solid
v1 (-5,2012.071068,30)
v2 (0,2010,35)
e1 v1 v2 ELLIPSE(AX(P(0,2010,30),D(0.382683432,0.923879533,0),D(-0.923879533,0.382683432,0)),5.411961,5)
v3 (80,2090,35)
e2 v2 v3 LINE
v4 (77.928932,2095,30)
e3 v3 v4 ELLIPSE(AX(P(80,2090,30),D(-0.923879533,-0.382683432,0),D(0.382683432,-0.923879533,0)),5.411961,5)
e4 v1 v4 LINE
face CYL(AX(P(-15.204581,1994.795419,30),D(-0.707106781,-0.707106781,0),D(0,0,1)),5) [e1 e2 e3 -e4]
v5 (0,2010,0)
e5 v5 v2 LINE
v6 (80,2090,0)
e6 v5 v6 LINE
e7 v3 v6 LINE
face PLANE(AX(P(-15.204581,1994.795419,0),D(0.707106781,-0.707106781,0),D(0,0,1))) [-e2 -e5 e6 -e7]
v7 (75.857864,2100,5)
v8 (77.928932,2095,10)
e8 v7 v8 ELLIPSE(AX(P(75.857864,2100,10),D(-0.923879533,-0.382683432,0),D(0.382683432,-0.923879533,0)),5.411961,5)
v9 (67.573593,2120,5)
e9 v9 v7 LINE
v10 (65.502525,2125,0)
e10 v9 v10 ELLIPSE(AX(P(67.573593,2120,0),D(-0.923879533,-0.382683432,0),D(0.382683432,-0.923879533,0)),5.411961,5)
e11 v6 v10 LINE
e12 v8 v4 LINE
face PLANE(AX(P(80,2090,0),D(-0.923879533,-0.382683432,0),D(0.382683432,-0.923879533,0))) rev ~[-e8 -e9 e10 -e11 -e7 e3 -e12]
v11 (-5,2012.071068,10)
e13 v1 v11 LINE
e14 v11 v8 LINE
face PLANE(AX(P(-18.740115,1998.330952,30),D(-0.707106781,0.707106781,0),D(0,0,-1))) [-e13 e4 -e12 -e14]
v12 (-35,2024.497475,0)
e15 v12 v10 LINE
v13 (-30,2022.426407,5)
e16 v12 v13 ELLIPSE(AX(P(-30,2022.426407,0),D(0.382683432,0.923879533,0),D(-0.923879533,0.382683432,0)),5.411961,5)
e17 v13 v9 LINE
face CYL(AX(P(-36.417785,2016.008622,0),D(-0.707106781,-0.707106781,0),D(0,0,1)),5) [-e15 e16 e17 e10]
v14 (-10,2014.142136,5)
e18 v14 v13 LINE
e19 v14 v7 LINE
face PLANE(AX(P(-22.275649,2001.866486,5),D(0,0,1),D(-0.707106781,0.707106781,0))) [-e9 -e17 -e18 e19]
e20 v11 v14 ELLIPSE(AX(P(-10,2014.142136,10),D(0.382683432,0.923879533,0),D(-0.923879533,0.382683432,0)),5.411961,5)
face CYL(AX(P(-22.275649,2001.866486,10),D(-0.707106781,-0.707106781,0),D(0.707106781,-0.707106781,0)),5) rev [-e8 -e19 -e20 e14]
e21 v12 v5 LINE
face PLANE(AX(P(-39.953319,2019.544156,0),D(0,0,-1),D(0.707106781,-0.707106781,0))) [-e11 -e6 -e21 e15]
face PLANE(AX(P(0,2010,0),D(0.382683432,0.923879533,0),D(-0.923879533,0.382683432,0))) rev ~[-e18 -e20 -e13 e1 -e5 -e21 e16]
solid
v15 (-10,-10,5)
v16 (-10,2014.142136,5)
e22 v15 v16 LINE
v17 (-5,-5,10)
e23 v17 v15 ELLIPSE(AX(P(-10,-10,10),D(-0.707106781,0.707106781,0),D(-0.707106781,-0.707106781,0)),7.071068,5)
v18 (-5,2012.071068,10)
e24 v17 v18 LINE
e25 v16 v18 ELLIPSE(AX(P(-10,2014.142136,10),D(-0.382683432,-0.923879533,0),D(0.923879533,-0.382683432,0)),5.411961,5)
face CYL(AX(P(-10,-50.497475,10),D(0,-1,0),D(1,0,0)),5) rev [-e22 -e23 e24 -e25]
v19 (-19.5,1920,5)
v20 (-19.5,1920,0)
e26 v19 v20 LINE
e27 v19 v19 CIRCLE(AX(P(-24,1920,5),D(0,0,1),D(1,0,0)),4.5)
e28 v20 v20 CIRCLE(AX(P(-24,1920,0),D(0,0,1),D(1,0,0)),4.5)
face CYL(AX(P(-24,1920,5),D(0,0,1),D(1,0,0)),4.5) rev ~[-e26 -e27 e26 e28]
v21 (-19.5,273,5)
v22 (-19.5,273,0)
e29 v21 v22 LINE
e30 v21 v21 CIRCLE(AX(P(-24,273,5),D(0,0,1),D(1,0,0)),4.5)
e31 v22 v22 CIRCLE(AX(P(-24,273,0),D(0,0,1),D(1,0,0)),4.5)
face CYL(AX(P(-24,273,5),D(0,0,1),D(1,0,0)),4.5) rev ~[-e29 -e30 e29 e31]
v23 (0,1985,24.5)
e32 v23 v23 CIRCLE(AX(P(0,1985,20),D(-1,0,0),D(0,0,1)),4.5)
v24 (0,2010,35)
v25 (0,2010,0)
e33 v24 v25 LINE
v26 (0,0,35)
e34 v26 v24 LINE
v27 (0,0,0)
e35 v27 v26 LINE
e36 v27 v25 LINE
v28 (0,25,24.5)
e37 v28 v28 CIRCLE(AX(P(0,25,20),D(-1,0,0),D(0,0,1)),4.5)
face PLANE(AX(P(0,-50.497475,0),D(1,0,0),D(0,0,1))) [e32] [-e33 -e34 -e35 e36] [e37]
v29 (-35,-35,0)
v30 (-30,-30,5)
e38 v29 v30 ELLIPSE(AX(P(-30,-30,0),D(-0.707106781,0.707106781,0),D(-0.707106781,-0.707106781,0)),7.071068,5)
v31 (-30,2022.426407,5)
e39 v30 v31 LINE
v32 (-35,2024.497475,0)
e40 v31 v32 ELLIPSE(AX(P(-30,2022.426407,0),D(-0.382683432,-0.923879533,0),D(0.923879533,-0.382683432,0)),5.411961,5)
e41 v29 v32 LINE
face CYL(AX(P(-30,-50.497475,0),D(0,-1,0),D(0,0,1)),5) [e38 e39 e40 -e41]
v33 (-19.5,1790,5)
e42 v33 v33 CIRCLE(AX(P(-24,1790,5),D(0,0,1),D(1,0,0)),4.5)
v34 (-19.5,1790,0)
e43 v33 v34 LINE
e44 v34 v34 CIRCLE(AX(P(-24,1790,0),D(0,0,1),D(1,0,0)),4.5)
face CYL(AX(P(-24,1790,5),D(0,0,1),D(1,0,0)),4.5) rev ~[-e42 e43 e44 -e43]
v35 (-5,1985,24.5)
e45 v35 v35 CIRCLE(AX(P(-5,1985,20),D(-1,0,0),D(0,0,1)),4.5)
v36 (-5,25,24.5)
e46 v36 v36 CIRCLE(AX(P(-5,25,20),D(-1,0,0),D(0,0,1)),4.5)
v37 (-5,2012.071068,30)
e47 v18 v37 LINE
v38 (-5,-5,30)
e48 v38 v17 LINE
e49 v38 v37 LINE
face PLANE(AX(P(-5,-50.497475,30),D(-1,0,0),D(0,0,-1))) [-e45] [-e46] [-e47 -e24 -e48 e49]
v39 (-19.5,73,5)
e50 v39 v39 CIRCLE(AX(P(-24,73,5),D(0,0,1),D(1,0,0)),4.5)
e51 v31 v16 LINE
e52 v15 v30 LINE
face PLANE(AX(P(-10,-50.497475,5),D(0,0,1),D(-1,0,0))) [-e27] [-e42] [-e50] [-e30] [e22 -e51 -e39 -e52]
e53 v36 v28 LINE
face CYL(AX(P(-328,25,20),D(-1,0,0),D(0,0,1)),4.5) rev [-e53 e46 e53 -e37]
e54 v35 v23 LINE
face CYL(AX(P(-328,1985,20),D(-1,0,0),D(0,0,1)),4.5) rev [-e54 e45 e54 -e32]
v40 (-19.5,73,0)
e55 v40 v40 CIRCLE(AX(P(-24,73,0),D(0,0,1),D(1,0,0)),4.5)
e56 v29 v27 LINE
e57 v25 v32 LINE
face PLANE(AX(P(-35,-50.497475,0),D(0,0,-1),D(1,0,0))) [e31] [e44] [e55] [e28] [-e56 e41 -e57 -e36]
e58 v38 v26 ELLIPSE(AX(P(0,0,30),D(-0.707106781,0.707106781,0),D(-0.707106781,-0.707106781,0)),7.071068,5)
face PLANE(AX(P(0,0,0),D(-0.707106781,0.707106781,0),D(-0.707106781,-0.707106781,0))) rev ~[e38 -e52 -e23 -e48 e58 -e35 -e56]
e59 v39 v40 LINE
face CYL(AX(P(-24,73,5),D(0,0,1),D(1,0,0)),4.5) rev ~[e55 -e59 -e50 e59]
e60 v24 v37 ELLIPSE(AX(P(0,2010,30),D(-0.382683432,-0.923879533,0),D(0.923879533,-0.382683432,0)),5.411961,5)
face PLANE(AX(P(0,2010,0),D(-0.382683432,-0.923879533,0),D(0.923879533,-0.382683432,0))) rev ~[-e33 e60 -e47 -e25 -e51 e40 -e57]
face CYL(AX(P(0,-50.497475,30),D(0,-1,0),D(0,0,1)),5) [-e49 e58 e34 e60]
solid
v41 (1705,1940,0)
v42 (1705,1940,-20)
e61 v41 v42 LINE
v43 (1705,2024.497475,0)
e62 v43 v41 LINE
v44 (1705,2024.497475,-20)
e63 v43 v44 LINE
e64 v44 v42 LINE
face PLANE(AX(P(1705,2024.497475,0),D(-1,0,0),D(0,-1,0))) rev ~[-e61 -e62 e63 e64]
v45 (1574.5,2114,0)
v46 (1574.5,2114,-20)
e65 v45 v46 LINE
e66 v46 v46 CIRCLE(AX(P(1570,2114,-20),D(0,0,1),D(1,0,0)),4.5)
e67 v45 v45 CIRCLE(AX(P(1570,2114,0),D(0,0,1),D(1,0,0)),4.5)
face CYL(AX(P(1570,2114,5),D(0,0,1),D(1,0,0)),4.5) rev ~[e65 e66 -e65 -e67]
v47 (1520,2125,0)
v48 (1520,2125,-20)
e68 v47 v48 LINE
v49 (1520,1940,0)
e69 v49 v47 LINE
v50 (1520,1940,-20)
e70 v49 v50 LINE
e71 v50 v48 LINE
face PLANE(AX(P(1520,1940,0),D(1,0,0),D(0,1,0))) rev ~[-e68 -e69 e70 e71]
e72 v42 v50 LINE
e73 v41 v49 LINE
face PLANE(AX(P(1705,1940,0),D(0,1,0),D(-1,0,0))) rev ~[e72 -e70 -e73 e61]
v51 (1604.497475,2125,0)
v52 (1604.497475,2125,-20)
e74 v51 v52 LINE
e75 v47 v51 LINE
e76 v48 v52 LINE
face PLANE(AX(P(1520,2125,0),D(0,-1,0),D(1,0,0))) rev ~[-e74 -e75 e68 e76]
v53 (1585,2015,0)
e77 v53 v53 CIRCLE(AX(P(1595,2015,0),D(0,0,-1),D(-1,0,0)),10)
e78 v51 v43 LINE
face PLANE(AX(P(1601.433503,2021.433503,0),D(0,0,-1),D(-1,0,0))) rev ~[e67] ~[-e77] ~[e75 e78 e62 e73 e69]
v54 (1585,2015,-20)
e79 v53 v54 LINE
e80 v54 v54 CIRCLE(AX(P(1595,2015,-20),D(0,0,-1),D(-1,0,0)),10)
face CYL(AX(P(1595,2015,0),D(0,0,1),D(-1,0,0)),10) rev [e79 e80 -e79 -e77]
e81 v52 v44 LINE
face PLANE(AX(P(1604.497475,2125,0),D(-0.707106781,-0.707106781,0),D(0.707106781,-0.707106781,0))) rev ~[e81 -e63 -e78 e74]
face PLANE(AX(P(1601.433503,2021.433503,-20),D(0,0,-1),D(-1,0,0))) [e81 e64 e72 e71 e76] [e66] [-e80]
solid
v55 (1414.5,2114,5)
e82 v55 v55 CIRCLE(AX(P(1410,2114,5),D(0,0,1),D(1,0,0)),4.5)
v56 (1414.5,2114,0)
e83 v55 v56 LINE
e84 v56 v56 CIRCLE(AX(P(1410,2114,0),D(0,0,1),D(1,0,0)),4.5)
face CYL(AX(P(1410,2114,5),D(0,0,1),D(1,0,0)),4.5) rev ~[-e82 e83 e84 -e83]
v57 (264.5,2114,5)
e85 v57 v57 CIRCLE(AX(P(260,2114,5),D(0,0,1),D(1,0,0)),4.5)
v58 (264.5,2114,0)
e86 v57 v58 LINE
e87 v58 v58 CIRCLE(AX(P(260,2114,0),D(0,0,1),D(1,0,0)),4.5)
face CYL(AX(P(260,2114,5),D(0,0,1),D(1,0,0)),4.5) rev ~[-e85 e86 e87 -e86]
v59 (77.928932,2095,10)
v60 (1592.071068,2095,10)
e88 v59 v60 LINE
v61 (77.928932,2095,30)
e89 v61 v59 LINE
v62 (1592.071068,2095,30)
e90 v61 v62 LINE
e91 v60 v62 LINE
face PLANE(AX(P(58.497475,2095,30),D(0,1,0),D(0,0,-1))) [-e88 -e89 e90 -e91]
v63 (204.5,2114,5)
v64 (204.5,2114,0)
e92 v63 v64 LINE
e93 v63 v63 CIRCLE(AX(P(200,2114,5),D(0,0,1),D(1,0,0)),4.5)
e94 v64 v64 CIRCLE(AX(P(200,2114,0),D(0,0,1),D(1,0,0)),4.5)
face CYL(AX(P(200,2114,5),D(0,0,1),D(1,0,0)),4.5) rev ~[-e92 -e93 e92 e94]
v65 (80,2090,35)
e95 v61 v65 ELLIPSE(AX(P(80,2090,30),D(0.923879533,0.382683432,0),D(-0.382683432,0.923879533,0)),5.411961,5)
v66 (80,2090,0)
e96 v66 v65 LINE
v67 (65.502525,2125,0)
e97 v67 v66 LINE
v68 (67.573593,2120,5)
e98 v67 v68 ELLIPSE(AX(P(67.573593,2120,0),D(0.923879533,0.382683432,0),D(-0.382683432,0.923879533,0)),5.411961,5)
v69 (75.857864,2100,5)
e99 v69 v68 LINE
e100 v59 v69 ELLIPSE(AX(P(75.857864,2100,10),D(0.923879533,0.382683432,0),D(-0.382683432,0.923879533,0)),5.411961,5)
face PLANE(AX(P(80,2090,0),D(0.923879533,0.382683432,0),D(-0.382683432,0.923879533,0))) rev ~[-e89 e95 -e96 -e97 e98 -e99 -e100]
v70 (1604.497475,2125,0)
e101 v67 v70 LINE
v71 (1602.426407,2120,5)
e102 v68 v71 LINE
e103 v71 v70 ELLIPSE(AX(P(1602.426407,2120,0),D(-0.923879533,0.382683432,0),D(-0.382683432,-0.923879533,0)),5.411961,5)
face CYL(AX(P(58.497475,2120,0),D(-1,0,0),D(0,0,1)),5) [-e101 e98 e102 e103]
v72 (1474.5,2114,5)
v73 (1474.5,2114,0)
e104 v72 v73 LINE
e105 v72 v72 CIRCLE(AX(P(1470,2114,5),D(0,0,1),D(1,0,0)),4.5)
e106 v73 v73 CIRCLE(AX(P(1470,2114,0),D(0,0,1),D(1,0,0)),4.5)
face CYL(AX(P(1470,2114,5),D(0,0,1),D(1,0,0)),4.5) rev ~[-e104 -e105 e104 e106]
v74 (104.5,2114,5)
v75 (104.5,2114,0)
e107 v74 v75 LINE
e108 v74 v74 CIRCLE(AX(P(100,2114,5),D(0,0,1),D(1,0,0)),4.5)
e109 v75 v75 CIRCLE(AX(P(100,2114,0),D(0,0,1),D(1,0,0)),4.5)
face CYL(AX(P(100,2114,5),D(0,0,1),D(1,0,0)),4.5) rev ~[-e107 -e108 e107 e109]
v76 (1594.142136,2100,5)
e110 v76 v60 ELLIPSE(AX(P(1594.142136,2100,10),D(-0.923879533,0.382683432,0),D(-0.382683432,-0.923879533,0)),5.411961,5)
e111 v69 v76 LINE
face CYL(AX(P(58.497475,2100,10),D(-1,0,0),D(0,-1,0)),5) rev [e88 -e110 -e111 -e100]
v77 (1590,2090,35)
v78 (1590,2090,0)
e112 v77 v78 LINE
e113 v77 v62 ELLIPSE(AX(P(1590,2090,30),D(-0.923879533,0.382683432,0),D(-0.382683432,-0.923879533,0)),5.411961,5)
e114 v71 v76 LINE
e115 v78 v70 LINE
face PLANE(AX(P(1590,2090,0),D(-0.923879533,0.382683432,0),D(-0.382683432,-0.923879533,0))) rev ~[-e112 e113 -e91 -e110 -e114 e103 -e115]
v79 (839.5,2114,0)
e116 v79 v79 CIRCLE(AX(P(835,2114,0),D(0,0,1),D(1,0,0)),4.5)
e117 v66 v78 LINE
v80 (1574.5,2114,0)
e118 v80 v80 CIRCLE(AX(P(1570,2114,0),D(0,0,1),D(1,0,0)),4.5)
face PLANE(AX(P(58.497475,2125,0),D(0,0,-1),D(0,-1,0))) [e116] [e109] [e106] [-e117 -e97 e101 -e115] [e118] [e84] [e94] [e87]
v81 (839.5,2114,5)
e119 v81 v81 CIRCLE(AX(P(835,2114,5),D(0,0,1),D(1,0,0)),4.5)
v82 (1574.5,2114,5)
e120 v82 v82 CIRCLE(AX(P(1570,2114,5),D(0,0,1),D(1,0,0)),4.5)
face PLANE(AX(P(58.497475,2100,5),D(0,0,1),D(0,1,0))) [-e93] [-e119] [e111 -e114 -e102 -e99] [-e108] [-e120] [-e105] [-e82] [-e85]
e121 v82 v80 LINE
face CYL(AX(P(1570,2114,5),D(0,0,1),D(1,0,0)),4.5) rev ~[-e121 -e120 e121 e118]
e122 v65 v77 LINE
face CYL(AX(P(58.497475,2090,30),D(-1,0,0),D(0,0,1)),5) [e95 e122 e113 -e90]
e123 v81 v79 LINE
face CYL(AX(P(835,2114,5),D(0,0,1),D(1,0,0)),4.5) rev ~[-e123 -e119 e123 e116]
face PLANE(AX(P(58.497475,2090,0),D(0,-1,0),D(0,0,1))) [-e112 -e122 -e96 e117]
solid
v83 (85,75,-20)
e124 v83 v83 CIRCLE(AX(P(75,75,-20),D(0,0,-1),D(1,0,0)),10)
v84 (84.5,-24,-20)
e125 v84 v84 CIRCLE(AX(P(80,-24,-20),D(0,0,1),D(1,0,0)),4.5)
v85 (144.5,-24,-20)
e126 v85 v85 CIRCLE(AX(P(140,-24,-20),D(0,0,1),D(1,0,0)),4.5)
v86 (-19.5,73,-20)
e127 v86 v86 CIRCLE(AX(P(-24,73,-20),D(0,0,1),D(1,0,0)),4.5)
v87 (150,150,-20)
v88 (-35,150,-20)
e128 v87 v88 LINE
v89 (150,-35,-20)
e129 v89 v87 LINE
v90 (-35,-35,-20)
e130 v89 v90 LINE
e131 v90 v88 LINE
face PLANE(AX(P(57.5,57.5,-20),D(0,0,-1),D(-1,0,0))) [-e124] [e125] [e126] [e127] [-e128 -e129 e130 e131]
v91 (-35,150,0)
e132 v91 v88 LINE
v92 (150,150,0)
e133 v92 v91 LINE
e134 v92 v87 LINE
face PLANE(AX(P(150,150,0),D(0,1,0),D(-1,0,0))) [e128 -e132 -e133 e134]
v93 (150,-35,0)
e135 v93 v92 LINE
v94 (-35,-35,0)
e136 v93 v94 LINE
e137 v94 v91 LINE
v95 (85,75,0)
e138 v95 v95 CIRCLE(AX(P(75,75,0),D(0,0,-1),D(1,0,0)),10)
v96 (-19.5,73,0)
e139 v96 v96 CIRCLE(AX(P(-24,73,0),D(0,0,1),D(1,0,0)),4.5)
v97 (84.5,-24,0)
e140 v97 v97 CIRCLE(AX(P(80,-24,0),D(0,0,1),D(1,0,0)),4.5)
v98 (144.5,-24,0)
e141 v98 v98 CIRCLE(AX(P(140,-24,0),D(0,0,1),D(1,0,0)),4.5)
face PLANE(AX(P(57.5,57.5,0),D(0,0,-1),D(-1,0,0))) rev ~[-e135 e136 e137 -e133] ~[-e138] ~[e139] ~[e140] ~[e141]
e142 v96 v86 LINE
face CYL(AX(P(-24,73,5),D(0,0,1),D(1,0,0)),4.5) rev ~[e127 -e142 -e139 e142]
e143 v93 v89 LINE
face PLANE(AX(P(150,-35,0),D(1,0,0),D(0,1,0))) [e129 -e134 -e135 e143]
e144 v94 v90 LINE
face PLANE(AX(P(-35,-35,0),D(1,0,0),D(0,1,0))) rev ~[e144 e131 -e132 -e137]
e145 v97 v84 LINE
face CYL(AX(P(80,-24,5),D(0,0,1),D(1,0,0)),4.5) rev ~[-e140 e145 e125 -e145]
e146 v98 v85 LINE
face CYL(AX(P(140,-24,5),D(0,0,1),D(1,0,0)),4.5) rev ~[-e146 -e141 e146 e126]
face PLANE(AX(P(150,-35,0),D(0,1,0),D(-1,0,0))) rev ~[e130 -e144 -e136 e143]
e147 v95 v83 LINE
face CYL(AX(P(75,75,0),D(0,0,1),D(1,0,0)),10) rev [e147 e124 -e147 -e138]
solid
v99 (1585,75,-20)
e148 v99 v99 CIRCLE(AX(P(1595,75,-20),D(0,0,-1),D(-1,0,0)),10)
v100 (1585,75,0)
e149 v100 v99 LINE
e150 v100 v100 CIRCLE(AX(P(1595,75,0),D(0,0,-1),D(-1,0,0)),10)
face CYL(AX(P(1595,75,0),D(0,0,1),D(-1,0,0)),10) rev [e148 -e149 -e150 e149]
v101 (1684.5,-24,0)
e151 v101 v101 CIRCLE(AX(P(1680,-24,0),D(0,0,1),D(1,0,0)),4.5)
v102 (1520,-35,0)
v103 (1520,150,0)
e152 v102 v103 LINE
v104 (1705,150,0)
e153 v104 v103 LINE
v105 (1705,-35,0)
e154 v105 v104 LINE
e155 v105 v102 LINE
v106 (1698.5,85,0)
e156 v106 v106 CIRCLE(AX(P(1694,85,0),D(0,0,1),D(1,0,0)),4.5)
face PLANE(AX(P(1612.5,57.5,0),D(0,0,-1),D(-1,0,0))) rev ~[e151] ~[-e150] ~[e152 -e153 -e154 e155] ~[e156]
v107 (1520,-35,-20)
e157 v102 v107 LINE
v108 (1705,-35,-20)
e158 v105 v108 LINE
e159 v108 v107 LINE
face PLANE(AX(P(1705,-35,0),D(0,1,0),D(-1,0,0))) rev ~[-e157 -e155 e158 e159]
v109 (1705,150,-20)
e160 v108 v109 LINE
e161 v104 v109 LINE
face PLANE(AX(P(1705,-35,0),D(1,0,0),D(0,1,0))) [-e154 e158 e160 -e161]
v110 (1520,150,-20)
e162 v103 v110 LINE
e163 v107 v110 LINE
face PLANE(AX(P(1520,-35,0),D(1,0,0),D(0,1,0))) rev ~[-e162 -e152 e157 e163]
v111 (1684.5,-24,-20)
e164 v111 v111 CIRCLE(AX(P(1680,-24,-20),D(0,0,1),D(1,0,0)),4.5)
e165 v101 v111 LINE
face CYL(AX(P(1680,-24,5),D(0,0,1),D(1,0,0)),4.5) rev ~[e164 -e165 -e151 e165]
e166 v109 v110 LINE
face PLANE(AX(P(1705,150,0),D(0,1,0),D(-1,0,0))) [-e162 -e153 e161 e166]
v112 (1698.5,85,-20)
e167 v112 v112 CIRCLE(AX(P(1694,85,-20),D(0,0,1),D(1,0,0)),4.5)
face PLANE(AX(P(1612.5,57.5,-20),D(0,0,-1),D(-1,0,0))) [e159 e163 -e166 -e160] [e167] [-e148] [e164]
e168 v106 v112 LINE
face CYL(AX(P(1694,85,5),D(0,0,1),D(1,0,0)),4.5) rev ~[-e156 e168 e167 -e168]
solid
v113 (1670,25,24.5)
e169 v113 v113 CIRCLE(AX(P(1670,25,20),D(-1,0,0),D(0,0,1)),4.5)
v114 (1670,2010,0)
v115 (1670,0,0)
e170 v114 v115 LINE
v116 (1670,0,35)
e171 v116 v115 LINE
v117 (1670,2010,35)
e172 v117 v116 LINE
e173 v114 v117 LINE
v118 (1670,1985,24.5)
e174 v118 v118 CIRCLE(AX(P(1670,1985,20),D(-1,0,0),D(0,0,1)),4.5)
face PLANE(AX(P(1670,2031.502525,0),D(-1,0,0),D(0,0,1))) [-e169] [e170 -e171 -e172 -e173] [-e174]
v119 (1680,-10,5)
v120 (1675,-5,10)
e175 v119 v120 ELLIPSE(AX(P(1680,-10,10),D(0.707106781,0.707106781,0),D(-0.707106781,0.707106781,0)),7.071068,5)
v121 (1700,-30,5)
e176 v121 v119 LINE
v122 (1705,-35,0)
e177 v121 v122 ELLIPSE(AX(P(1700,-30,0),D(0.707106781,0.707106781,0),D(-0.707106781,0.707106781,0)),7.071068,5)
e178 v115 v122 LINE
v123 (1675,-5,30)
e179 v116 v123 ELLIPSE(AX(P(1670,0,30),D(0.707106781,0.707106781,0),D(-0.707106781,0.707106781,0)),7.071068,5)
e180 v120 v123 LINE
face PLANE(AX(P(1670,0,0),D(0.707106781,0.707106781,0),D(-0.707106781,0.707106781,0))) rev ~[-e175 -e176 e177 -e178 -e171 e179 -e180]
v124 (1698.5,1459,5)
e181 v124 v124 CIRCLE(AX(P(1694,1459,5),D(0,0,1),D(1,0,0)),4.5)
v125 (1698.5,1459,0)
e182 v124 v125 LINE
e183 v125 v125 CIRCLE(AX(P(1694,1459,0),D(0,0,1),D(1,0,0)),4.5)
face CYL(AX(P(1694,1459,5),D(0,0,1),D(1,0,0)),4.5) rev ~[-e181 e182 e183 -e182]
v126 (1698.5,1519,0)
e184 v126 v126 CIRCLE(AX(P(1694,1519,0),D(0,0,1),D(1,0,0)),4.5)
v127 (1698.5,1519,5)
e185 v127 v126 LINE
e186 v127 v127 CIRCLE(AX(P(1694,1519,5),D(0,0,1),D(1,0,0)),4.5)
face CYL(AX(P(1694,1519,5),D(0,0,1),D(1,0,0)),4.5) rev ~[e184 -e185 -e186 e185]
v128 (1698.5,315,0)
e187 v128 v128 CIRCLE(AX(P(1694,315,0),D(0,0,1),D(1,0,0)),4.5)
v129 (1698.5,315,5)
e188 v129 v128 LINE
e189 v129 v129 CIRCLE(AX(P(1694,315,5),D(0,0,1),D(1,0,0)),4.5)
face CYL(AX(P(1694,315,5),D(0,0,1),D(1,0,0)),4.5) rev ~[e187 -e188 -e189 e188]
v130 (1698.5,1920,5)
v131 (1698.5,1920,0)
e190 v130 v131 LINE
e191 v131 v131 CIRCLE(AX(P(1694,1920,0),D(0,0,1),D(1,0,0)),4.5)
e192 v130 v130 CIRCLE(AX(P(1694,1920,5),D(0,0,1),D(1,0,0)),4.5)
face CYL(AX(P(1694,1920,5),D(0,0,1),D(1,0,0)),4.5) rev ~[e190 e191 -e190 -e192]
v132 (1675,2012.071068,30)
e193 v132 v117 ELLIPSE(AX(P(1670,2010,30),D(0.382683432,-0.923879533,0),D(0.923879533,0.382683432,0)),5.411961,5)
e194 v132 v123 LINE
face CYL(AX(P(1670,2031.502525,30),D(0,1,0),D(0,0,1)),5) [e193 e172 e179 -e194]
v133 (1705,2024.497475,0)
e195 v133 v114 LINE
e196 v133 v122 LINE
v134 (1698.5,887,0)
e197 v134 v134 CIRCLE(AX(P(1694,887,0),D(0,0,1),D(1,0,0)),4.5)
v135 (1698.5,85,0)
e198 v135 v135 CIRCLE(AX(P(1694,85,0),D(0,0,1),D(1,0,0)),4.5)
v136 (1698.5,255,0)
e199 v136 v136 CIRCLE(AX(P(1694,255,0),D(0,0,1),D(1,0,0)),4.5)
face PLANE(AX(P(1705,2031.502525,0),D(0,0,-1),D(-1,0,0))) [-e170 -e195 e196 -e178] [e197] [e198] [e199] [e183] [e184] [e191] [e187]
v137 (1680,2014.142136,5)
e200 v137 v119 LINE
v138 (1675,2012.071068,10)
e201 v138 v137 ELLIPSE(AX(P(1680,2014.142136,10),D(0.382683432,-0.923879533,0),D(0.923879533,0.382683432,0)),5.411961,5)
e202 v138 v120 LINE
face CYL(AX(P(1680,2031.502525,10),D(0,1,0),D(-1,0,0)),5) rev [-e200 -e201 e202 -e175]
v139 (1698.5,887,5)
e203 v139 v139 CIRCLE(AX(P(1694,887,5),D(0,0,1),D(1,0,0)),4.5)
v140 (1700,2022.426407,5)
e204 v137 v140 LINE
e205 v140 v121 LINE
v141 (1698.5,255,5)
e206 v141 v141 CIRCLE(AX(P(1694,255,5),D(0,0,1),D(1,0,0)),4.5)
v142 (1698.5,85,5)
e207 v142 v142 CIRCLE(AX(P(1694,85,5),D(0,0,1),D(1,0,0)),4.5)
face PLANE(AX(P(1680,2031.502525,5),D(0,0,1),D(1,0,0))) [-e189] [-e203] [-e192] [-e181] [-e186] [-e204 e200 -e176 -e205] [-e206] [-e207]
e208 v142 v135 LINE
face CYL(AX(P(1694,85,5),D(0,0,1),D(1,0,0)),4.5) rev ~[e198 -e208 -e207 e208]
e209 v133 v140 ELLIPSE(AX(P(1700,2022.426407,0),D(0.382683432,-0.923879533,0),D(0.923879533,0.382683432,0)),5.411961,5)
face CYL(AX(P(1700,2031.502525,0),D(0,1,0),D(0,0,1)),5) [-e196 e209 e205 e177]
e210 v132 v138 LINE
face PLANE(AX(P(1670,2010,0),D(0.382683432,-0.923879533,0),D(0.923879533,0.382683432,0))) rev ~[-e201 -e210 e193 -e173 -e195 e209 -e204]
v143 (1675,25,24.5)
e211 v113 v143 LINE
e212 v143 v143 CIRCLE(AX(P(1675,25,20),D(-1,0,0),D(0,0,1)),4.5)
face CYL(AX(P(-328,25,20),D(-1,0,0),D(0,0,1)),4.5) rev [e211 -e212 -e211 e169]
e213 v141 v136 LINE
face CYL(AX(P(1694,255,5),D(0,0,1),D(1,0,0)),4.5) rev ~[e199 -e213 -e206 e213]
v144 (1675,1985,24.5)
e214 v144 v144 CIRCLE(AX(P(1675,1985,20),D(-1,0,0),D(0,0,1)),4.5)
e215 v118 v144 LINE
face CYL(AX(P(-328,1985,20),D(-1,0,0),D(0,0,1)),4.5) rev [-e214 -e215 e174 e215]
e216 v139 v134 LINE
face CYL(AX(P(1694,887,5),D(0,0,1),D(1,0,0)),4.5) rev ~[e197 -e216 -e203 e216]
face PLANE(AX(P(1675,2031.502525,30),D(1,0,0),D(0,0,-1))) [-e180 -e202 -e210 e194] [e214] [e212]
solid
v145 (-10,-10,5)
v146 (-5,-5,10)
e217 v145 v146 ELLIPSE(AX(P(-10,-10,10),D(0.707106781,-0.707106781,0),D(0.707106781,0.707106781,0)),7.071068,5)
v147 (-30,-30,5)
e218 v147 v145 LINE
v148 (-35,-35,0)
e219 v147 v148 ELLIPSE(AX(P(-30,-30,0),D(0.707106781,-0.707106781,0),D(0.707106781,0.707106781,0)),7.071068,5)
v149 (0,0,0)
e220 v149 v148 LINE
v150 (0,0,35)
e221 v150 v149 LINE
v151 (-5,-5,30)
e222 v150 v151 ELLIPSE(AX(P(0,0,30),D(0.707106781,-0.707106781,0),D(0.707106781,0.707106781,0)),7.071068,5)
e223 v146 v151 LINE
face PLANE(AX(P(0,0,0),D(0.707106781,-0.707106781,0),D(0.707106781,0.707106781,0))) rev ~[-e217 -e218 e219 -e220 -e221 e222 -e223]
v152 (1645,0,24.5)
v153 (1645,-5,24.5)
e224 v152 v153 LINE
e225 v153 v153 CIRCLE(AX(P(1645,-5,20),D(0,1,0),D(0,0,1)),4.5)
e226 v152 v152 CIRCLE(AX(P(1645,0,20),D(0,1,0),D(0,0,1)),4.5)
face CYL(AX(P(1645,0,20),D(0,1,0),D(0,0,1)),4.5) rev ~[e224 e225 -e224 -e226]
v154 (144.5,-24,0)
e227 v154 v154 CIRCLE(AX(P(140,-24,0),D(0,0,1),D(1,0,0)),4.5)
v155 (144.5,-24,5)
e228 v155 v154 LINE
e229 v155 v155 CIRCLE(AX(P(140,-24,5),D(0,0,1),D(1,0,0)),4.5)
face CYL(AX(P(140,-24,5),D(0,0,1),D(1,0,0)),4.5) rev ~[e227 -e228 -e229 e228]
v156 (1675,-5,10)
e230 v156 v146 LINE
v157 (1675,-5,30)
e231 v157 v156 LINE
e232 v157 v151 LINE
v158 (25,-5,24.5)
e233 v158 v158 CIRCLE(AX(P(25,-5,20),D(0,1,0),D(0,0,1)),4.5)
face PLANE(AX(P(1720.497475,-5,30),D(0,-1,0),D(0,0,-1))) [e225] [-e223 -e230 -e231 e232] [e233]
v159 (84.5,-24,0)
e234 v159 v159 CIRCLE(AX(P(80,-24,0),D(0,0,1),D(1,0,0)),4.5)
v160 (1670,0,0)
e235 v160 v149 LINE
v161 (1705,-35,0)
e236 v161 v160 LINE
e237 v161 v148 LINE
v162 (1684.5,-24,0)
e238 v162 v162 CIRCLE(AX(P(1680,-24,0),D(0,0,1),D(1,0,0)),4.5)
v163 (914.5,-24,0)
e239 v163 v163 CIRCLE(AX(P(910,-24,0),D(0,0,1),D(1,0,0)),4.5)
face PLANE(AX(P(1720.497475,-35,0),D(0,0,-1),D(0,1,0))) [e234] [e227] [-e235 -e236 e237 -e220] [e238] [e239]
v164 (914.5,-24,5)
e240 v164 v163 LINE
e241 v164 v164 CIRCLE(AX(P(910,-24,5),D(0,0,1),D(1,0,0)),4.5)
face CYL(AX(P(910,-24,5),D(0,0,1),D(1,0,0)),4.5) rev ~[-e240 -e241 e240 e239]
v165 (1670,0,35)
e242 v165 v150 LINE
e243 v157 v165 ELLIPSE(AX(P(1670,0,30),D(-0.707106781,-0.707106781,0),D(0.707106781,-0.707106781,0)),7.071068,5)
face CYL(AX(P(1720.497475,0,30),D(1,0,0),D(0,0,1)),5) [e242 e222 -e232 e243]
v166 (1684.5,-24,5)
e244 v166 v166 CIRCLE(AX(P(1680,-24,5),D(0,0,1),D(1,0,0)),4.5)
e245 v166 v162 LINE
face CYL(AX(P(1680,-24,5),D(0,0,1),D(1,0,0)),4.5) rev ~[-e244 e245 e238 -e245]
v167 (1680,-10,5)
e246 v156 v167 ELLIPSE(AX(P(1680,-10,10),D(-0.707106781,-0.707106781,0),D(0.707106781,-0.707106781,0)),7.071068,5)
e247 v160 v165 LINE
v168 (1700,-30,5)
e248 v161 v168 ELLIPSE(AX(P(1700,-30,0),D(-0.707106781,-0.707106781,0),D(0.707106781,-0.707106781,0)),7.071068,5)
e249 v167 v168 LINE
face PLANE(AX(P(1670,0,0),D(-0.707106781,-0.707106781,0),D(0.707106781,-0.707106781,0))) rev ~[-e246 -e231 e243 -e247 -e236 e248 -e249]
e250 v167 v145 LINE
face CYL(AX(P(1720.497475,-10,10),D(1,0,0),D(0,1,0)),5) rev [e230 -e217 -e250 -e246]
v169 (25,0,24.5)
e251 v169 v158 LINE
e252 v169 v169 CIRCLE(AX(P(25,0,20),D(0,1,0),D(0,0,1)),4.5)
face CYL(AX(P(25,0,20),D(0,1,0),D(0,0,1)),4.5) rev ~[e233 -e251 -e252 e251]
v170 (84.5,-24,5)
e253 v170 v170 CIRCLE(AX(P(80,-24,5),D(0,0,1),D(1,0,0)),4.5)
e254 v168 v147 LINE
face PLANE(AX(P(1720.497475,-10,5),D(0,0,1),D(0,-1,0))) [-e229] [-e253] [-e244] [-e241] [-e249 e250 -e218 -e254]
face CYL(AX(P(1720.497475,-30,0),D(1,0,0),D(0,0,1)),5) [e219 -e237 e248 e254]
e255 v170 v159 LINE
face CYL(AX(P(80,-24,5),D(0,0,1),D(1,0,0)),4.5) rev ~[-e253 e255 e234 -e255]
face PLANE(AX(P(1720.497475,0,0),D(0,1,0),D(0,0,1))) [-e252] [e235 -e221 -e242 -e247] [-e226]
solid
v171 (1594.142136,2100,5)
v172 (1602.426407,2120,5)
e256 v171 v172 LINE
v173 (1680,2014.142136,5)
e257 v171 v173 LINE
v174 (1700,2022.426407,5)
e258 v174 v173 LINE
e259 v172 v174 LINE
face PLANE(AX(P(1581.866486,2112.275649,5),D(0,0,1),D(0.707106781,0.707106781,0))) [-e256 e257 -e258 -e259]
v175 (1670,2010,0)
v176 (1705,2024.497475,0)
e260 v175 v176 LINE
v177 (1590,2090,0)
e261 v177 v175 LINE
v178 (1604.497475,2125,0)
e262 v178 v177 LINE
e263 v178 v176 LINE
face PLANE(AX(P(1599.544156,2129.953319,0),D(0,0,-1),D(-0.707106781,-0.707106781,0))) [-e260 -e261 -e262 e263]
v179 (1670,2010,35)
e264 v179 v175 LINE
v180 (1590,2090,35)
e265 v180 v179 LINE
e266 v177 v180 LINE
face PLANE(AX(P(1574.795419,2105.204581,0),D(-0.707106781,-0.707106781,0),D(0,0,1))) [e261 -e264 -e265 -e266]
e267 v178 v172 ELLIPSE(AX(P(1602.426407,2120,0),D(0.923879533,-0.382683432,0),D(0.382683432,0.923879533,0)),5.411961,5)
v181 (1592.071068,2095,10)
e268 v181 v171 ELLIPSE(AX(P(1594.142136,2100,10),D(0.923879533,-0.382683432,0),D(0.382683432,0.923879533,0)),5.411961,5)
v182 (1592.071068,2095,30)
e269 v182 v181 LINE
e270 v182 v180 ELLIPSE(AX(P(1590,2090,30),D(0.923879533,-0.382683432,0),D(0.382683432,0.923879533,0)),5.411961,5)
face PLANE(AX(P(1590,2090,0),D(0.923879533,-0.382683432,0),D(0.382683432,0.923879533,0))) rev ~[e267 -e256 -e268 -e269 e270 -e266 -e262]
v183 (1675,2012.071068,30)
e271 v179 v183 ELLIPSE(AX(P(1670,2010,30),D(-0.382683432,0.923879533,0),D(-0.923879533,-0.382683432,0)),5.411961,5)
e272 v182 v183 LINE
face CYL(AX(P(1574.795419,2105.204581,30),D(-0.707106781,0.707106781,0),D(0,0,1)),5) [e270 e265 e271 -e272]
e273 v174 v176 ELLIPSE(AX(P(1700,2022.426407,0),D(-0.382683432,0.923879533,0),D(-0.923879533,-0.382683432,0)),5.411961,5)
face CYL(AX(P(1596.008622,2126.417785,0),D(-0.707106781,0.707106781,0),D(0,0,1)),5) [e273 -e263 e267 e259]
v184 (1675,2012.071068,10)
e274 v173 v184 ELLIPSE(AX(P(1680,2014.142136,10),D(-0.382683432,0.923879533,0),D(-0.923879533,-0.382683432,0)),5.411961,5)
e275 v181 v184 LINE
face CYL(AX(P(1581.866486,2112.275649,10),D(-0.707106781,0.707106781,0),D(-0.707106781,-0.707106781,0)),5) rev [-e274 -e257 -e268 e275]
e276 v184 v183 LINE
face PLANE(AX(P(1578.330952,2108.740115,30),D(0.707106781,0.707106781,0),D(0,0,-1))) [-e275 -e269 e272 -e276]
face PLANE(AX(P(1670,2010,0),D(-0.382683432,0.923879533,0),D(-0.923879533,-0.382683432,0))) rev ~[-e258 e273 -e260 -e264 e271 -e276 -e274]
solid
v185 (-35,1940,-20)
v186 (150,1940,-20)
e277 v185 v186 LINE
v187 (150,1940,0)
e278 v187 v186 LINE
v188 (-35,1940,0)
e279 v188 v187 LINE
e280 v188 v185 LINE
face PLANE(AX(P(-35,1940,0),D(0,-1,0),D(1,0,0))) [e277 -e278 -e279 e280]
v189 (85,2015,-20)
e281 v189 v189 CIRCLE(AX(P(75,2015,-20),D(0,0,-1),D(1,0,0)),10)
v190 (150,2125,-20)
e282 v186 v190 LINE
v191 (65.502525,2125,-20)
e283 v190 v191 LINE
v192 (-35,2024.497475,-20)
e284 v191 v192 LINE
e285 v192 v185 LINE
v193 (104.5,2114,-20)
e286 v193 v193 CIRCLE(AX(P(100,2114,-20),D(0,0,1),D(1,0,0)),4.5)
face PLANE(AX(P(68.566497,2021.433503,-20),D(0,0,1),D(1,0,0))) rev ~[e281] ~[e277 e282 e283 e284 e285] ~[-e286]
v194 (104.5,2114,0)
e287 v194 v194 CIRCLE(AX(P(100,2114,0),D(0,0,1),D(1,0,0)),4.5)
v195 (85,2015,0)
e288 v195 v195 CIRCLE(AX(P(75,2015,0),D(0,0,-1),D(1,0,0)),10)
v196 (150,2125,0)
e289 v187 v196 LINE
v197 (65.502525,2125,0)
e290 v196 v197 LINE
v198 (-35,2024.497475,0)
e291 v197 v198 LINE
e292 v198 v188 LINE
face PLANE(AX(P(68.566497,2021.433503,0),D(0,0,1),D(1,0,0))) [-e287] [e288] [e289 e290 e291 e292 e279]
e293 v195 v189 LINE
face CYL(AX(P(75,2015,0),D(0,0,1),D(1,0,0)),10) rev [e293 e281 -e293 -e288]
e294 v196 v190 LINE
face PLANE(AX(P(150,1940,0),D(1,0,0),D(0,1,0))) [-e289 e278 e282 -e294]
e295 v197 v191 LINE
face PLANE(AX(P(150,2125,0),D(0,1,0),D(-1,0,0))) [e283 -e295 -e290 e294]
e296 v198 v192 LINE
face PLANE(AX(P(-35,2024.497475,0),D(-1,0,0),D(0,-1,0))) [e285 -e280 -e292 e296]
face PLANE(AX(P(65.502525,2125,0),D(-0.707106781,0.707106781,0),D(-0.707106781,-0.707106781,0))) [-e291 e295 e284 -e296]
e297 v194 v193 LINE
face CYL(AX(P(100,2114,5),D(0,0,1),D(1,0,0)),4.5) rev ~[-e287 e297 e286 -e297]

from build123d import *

# Parameters (mm, degrees)
MEMBER_1_DEPTH           = 2031.502525317
MEMBER_1_DEPTH_BACK      = 50.497474683
MEMBER_1_2_DEPTH         = 156.142135624
MEMBER_1_3_DEPTH         = 1553.005050634
MEMBER_1_4_DEPTH         = 156.142135624
MEMBER_1_5_DEPTH         = 2082
MEMBER_1_6_DEPTH         = 1770.994949366
SKETCH_3_R               = 10
EXTRUDE_1_DEPTH          = 20
SKETCH_3_W               = 185
SKETCH_3_H               = 185
EXTRUDE_1_2_DEPTH        = 20
EXTRUDE_1_3_DEPTH        = 20
EXTRUDE_1_4_DEPTH        = 20
SKETCH_4_R               = 4.5
CUT_EXTRUDE_1_DEPTH      = 10
CUT_EXTRUDE_2_DEPTH      = 2262
CUT_EXTRUDE_2_DEPTH_BACK = 328
SKETCH_5_R               = 4.5
SKETCH_6_R               = 4.5
CUT_EXTRUDE_3_DEPTH      = 236
SKETCH_7_R               = 4.5
CUT_EXTRUDE_4_DEPTH      = 228
SKETCH_8_R               = 4.5
CUT_EXTRUDE_5_DEPTH      = 99
SKETCH_9_R               = 4.5
CUT_EXTRUDE_6_DEPTH      = 78


with BuildPart() as part:
    # Sketch1 → Member 1 (new, two sides: drawn at the far end of the back side and taken through both)
    with BuildSketch(Plane(origin=(0, 0, 0), x_dir=(-1, 0, 0), z_dir=(0, 1, 0)).offset(-MEMBER_1_DEPTH_BACK)):
        with BuildLine():
            Line((0, 0), (0, 35))
            ThreePointArc((0, 35), (3.535533906, 33.535533906), (5, 30))
            Line((5, 30), (5, 10))
            ThreePointArc((5, 10), (6.464466094, 6.464466094), (10, 5))
            Line((10, 5), (30, 5))
            ThreePointArc((30, 5), (33.535533906, 3.535533906), (35, 0))
            Line((35, 0), (0, 0))
        make_face()
    extrude(amount=MEMBER_1_DEPTH + MEMBER_1_DEPTH_BACK)

    # Member 1 mitre 1
    split(bisect_by=Plane(origin=(0, 0, 0), x_dir=(-0.707106781, -0.707106781, 0), z_dir=(-0.707106781, 0.707106781, 0)), keep=Keep.TOP)

    # Member 1 mitre 2
    split(bisect_by=Plane(origin=(0, 2010, 0), x_dir=(0.923879533, -0.382683432, 0), z_dir=(-0.382683432, -0.923879533, 0)), keep=Keep.TOP)


with BuildPart() as body_2:
    # Sketch1 on segment 2 (carried to segment 2) → Member 1 2 (new body)
    with BuildSketch(Plane(origin=(-15.204581464, 1994.795418536, 0), x_dir=(-0.707106781, 0.707106781, 0), z_dir=(0.707106781, 0.707106781, 0))):
        with BuildLine():
            Line((0, 0), (0, 35))
            ThreePointArc((0, 35), (3.535533906, 33.535533906), (5, 30))
            Line((5, 30), (5, 10))
            ThreePointArc((5, 10), (6.464466094, 6.464466094), (10, 5))
            Line((10, 5), (30, 5))
            ThreePointArc((30, 5), (33.535533906, 3.535533906), (35, 0))
            Line((35, 0), (0, 0))
        make_face()
    extrude(amount=MEMBER_1_2_DEPTH)

    # Member 1 2 mitre 1
    split(bisect_by=Plane(origin=(0, 2010, 0), x_dir=(-0.923879533, 0.382683432, 0), z_dir=(0.382683432, 0.923879533, 0)), keep=Keep.TOP)

    # Member 1 2 mitre 2
    split(bisect_by=Plane(origin=(80, 2090, 0), x_dir=(0.382683432, -0.923879533, 0), z_dir=(-0.923879533, -0.382683432, 0)), keep=Keep.TOP)


with BuildPart() as body_3:
    # Sketch1 on segment 3 (carried to segment 3) → Member 1 3 (new body)
    with BuildSketch(Plane(origin=(58.497474683, 2090, 0), x_dir=(0, 1, 0), z_dir=(1, 0, 0))):
        with BuildLine():
            Line((0, 0), (0, 35))
            ThreePointArc((0, 35), (3.535533906, 33.535533906), (5, 30))
            Line((5, 30), (5, 10))
            ThreePointArc((5, 10), (6.464466094, 6.464466094), (10, 5))
            Line((10, 5), (30, 5))
            ThreePointArc((30, 5), (33.535533906, 3.535533906), (35, 0))
            Line((35, 0), (0, 0))
        make_face()
    extrude(amount=MEMBER_1_3_DEPTH)

    # Member 1 3 mitre 1
    split(bisect_by=Plane(origin=(80, 2090, 0), x_dir=(-0.382683432, 0.923879533, 0), z_dir=(0.923879533, 0.382683432, 0)), keep=Keep.TOP)

    # Member 1 3 mitre 2
    split(bisect_by=Plane(origin=(1590, 2090, 0), x_dir=(-0.382683432, -0.923879533, 0), z_dir=(-0.923879533, 0.382683432, 0)), keep=Keep.TOP)


with BuildPart() as body_4:
    # Sketch1 on segment 4 (carried to segment 4) → Member 1 4 (new body)
    with BuildSketch(Plane(origin=(1574.795418536, 2105.204581464, 0), x_dir=(0.707106781, 0.707106781, 0), z_dir=(0.707106781, -0.707106781, 0))):
        with BuildLine():
            Line((0, 0), (0, 35))
            ThreePointArc((0, 35), (3.535533906, 33.535533906), (5, 30))
            Line((5, 30), (5, 10))
            ThreePointArc((5, 10), (6.464466094, 6.464466094), (10, 5))
            Line((10, 5), (30, 5))
            ThreePointArc((30, 5), (33.535533906, 3.535533906), (35, 0))
            Line((35, 0), (0, 0))
        make_face()
    extrude(amount=MEMBER_1_4_DEPTH)

    # Member 1 4 mitre 1
    split(bisect_by=Plane(origin=(1590, 2090, 0), x_dir=(0.382683432, 0.923879533, 0), z_dir=(0.923879533, -0.382683432, 0)), keep=Keep.TOP)

    # Member 1 4 mitre 2
    split(bisect_by=Plane(origin=(1670, 2010, 0), x_dir=(-0.923879533, -0.382683432, 0), z_dir=(-0.382683432, 0.923879533, 0)), keep=Keep.TOP)


with BuildPart() as body_5:
    # Sketch1 on segment 5 (carried to segment 5) → Member 1 5 (new body)
    with BuildSketch(Plane(origin=(1670, 2031.502525317, 0), x_dir=(1, 0, 0), z_dir=(0, -1, 0))):
        with BuildLine():
            Line((0, 0), (0, 35))
            ThreePointArc((0, 35), (3.535533906, 33.535533906), (5, 30))
            Line((5, 30), (5, 10))
            ThreePointArc((5, 10), (6.464466094, 6.464466094), (10, 5))
            Line((10, 5), (30, 5))
            ThreePointArc((30, 5), (33.535533906, 3.535533906), (35, 0))
            Line((35, 0), (0, 0))
        make_face()
    extrude(amount=MEMBER_1_5_DEPTH)

    # Member 1 5 mitre 1
    split(bisect_by=Plane(origin=(1670, 0, 0), x_dir=(-0.707106781, 0.707106781, 0), z_dir=(0.707106781, 0.707106781, 0)), keep=Keep.TOP)

    # Member 1 5 mitre 2
    split(bisect_by=Plane(origin=(1670, 2010, 0), x_dir=(0.923879533, 0.382683432, 0), z_dir=(0.382683432, -0.923879533, 0)), keep=Keep.TOP)


with BuildPart() as body_6:
    # Sketch1 on segment 6 (carried to segment 6) → Member 1 6 (new body)
    with BuildSketch(Plane(origin=(1720.497474683, 0, 0), x_dir=(0, -1, 0), z_dir=(-1, 0, 0))):
        with BuildLine():
            Line((0, 0), (0, 35))
            ThreePointArc((0, 35), (3.535533906, 33.535533906), (5, 30))
            Line((5, 30), (5, 10))
            ThreePointArc((5, 10), (6.464466094, 6.464466094), (10, 5))
            Line((10, 5), (30, 5))
            ThreePointArc((30, 5), (33.535533906, 3.535533906), (35, 0))
            Line((35, 0), (0, 0))
        make_face()
    extrude(amount=MEMBER_1_6_DEPTH)

    # Member 1 6 mitre 1
    split(bisect_by=Plane(origin=(0, 0, 0), x_dir=(0.707106781, 0.707106781, 0), z_dir=(0.707106781, -0.707106781, 0)), keep=Keep.TOP)

    # Member 1 6 mitre 2
    split(bisect_by=Plane(origin=(1670, 0, 0), x_dir=(0.707106781, -0.707106781, 0), z_dir=(-0.707106781, -0.707106781, 0)), keep=Keep.TOP)

    # 草图4 → 切除-拉伸1 (cut)
    with BuildSketch(Plane(origin=(0, 0, 0), x_dir=(1, 0, 0), z_dir=(0, 1, 0))):
        with Locations(Location((25, -20, 0), (0, 0, 270))):
            Circle(SKETCH_4_R)
        with Locations(Location((1645, -20, 0), (0, 0, 270))):
            Circle(SKETCH_4_R)
    extrude(amount=-CUT_EXTRUDE_1_DEPTH, mode=Mode.SUBTRACT)


with BuildPart() as body_7:
    # 草图3 → 凸台-拉伸1 (new body)
    with BuildSketch(Plane(origin=(0, 0, 0), x_dir=(-1, 0, 0), z_dir=(0, 0, -1))):
        Polygon((-1604.497474683, 2125), (-1705, 2024.497474683), (-1705, 1940), (-1520, 1940), (-1520, 2125), align=None)
        with Locations((-1595, 2015)):
            Circle(SKETCH_3_R, mode=Mode.SUBTRACT)
    extrude(amount=EXTRUDE_1_DEPTH)


with BuildPart() as body_8:
    # 草图3 → Extrude 1 2 (new body)
    with BuildSketch(Plane(origin=(0, 0, 0), x_dir=(-1, 0, 0), z_dir=(0, 0, -1))):
        with Locations((-1612.5, 57.5)):
            Rectangle(SKETCH_3_W, SKETCH_3_H)
        with Locations((-1595, 75)):
            Circle(SKETCH_3_R, mode=Mode.SUBTRACT)
    extrude(amount=EXTRUDE_1_2_DEPTH)


with BuildPart() as body_9:
    # 草图3 → Extrude 1 3 (new body)
    with BuildSketch(Plane(origin=(0, 0, 0), x_dir=(-1, 0, 0), z_dir=(0, 0, -1))):
        with Locations((-57.5, 57.5)):
            Rectangle(SKETCH_3_W, SKETCH_3_H)
        with Locations(Location((-75, 75, 0), (0, 0, 180))):
            Circle(SKETCH_3_R, mode=Mode.SUBTRACT)
    extrude(amount=EXTRUDE_1_3_DEPTH)


with BuildPart() as body_10:
    # 草图3 → Extrude 1 4 (new body)
    with BuildSketch(Plane(origin=(0, 0, 0), x_dir=(-1, 0, 0), z_dir=(0, 0, -1))):
        Polygon((-150, 2125), (-65.502525317, 2125), (35, 2024.497474683), (35, 1940), (-150, 1940), align=None)
        with Locations(Location((-75, 2015, 0), (0, 0, 180))):
            Circle(SKETCH_3_R, mode=Mode.SUBTRACT)
    extrude(amount=EXTRUDE_1_4_DEPTH)


with BuildPart() as cut_extrude_2_tool:
    # 草图5 → 切除-拉伸2 (new, two sides: drawn at the far end of the back side and taken through both)
    with BuildSketch(Plane(origin=(0, 0, 0), x_dir=(0, 0, -1), z_dir=(1, 0, 0)).offset(-CUT_EXTRUDE_2_DEPTH_BACK)):
        with Locations(Location((-20, 25, 0), (0, 0, 180))):
            Circle(SKETCH_5_R)
        with Locations(Location((-20, 1985, 0), (0, 0, 180))):
            Circle(SKETCH_5_R)
    extrude(amount=CUT_EXTRUDE_2_DEPTH + CUT_EXTRUDE_2_DEPTH_BACK)


with BuildPart() as part_1:
    add(part.part)

    # 切除-拉伸2: cut by cut_extrude_2_tool
    add(cut_extrude_2_tool.part, mode=Mode.SUBTRACT)


with BuildPart() as body_5_1:
    add(body_5.part)

    # 切除-拉伸2: cut by cut_extrude_2_tool
    add(cut_extrude_2_tool.part, mode=Mode.SUBTRACT)


with BuildPart() as cut_extrude_3_tool:
    # 草图6 → 切除-拉伸3 (new body)
    with BuildSketch(Plane.XY.offset(5)):
        with Locations((100, 2114)):
            Circle(SKETCH_6_R)
        with Locations((200, 2114)):
            Circle(SKETCH_6_R)
        with Locations((-24, 1920)):
            Circle(SKETCH_6_R)
        with Locations((-24, 1790)):
            Circle(SKETCH_6_R)
        with Locations((1470, 2114)):
            Circle(SKETCH_6_R)
        with Locations((1570, 2114)):
            Circle(SKETCH_6_R)
        with Locations((1694, 1920)):
            Circle(SKETCH_6_R)
        with Locations((1694, 1519)):
            Circle(SKETCH_6_R)
        with Locations((260, 2114)):
            Circle(SKETCH_6_R)
        with Locations((835, 2114)):
            Circle(SKETCH_6_R)
        with Locations((1410, 2114)):
            Circle(SKETCH_6_R)
    extrude(amount=-CUT_EXTRUDE_3_DEPTH)


with BuildPart() as part_2:
    add(part_1.part)

    # 切除-拉伸3: cut by cut_extrude_3_tool
    add(cut_extrude_3_tool.part, mode=Mode.SUBTRACT)


with BuildPart() as body_3_1:
    add(body_3.part)

    # 切除-拉伸3: cut by cut_extrude_3_tool
    add(cut_extrude_3_tool.part, mode=Mode.SUBTRACT)


with BuildPart() as body_5_2:
    add(body_5_1.part)

    # 切除-拉伸3: cut by cut_extrude_3_tool
    add(cut_extrude_3_tool.part, mode=Mode.SUBTRACT)


with BuildPart() as body_7_1:
    add(body_7.part)

    # 切除-拉伸3: cut by cut_extrude_3_tool
    add(cut_extrude_3_tool.part, mode=Mode.SUBTRACT)


with BuildPart() as body_10_1:
    add(body_10.part)

    # 切除-拉伸3: cut by cut_extrude_3_tool
    add(cut_extrude_3_tool.part, mode=Mode.SUBTRACT)


with BuildPart() as cut_extrude_4_tool:
    # 草图7 → 切除-拉伸4 (new body)
    with BuildSketch(Plane.XY.offset(5)):
        with Locations((-24, 73)):
            Circle(SKETCH_7_R)
        with Locations((-24, 273)):
            Circle(SKETCH_7_R)
        with Locations((80, -24)):
            Circle(SKETCH_7_R)
    extrude(amount=-CUT_EXTRUDE_4_DEPTH)


with BuildPart() as part_3:
    add(part_2.part)

    # 切除-拉伸4: cut by cut_extrude_4_tool
    add(cut_extrude_4_tool.part, mode=Mode.SUBTRACT)


with BuildPart() as body_6_1:
    add(body_6.part)

    # 切除-拉伸4: cut by cut_extrude_4_tool
    add(cut_extrude_4_tool.part, mode=Mode.SUBTRACT)


with BuildPart() as body_9_1:
    add(body_9.part)

    # 切除-拉伸4: cut by cut_extrude_4_tool
    add(cut_extrude_4_tool.part, mode=Mode.SUBTRACT)


with BuildPart() as cut_extrude_5_tool:
    # 草图8 → 切除-拉伸5 (new body)
    with BuildSketch(Plane.XY.offset(5)):
        with Locations((1694, 255)):
            Circle(SKETCH_8_R)
        with Locations((1694, 85)):
            Circle(SKETCH_8_R)
        with Locations((1694, 315)):
            Circle(SKETCH_8_R)
        with Locations((1694, 887)):
            Circle(SKETCH_8_R)
        with Locations((1694, 1459)):
            Circle(SKETCH_8_R)
    extrude(amount=-CUT_EXTRUDE_5_DEPTH)


with BuildPart() as body_5_3:
    add(body_5_2.part)

    # 切除-拉伸5: cut by cut_extrude_5_tool
    add(cut_extrude_5_tool.part, mode=Mode.SUBTRACT)


with BuildPart() as body_8_1:
    add(body_8.part)

    # 切除-拉伸5: cut by cut_extrude_5_tool
    add(cut_extrude_5_tool.part, mode=Mode.SUBTRACT)


with BuildPart() as cut_extrude_6_tool:
    # 草图9 → 切除-拉伸6 (new body)
    with BuildSketch(Plane.XY.offset(5)):
        with Locations((1680, -24)):
            Circle(SKETCH_9_R)
        with Locations((140, -24)):
            Circle(SKETCH_9_R)
        with Locations((910, -24)):
            Circle(SKETCH_9_R)
    extrude(amount=-CUT_EXTRUDE_6_DEPTH)


with BuildPart() as body_6_2:
    add(body_6_1.part)

    # 切除-拉伸6: cut by cut_extrude_6_tool
    add(cut_extrude_6_tool.part, mode=Mode.SUBTRACT)


with BuildPart() as body_8_2:
    add(body_8_1.part)

    # 切除-拉伸6: cut by cut_extrude_6_tool
    add(cut_extrude_6_tool.part, mode=Mode.SUBTRACT)


with BuildPart() as body_9_2:
    add(body_9_1.part)

    # 切除-拉伸6: cut by cut_extrude_6_tool
    add(cut_extrude_6_tool.part, mode=Mode.SUBTRACT)


solid = Compound([body_2.part, body_4.part, body_3_1.part, body_7_1.part, body_10_1.part, part_3.part, body_5_3.part, body_6_2.part, body_8_2.part, body_9_2.part])
